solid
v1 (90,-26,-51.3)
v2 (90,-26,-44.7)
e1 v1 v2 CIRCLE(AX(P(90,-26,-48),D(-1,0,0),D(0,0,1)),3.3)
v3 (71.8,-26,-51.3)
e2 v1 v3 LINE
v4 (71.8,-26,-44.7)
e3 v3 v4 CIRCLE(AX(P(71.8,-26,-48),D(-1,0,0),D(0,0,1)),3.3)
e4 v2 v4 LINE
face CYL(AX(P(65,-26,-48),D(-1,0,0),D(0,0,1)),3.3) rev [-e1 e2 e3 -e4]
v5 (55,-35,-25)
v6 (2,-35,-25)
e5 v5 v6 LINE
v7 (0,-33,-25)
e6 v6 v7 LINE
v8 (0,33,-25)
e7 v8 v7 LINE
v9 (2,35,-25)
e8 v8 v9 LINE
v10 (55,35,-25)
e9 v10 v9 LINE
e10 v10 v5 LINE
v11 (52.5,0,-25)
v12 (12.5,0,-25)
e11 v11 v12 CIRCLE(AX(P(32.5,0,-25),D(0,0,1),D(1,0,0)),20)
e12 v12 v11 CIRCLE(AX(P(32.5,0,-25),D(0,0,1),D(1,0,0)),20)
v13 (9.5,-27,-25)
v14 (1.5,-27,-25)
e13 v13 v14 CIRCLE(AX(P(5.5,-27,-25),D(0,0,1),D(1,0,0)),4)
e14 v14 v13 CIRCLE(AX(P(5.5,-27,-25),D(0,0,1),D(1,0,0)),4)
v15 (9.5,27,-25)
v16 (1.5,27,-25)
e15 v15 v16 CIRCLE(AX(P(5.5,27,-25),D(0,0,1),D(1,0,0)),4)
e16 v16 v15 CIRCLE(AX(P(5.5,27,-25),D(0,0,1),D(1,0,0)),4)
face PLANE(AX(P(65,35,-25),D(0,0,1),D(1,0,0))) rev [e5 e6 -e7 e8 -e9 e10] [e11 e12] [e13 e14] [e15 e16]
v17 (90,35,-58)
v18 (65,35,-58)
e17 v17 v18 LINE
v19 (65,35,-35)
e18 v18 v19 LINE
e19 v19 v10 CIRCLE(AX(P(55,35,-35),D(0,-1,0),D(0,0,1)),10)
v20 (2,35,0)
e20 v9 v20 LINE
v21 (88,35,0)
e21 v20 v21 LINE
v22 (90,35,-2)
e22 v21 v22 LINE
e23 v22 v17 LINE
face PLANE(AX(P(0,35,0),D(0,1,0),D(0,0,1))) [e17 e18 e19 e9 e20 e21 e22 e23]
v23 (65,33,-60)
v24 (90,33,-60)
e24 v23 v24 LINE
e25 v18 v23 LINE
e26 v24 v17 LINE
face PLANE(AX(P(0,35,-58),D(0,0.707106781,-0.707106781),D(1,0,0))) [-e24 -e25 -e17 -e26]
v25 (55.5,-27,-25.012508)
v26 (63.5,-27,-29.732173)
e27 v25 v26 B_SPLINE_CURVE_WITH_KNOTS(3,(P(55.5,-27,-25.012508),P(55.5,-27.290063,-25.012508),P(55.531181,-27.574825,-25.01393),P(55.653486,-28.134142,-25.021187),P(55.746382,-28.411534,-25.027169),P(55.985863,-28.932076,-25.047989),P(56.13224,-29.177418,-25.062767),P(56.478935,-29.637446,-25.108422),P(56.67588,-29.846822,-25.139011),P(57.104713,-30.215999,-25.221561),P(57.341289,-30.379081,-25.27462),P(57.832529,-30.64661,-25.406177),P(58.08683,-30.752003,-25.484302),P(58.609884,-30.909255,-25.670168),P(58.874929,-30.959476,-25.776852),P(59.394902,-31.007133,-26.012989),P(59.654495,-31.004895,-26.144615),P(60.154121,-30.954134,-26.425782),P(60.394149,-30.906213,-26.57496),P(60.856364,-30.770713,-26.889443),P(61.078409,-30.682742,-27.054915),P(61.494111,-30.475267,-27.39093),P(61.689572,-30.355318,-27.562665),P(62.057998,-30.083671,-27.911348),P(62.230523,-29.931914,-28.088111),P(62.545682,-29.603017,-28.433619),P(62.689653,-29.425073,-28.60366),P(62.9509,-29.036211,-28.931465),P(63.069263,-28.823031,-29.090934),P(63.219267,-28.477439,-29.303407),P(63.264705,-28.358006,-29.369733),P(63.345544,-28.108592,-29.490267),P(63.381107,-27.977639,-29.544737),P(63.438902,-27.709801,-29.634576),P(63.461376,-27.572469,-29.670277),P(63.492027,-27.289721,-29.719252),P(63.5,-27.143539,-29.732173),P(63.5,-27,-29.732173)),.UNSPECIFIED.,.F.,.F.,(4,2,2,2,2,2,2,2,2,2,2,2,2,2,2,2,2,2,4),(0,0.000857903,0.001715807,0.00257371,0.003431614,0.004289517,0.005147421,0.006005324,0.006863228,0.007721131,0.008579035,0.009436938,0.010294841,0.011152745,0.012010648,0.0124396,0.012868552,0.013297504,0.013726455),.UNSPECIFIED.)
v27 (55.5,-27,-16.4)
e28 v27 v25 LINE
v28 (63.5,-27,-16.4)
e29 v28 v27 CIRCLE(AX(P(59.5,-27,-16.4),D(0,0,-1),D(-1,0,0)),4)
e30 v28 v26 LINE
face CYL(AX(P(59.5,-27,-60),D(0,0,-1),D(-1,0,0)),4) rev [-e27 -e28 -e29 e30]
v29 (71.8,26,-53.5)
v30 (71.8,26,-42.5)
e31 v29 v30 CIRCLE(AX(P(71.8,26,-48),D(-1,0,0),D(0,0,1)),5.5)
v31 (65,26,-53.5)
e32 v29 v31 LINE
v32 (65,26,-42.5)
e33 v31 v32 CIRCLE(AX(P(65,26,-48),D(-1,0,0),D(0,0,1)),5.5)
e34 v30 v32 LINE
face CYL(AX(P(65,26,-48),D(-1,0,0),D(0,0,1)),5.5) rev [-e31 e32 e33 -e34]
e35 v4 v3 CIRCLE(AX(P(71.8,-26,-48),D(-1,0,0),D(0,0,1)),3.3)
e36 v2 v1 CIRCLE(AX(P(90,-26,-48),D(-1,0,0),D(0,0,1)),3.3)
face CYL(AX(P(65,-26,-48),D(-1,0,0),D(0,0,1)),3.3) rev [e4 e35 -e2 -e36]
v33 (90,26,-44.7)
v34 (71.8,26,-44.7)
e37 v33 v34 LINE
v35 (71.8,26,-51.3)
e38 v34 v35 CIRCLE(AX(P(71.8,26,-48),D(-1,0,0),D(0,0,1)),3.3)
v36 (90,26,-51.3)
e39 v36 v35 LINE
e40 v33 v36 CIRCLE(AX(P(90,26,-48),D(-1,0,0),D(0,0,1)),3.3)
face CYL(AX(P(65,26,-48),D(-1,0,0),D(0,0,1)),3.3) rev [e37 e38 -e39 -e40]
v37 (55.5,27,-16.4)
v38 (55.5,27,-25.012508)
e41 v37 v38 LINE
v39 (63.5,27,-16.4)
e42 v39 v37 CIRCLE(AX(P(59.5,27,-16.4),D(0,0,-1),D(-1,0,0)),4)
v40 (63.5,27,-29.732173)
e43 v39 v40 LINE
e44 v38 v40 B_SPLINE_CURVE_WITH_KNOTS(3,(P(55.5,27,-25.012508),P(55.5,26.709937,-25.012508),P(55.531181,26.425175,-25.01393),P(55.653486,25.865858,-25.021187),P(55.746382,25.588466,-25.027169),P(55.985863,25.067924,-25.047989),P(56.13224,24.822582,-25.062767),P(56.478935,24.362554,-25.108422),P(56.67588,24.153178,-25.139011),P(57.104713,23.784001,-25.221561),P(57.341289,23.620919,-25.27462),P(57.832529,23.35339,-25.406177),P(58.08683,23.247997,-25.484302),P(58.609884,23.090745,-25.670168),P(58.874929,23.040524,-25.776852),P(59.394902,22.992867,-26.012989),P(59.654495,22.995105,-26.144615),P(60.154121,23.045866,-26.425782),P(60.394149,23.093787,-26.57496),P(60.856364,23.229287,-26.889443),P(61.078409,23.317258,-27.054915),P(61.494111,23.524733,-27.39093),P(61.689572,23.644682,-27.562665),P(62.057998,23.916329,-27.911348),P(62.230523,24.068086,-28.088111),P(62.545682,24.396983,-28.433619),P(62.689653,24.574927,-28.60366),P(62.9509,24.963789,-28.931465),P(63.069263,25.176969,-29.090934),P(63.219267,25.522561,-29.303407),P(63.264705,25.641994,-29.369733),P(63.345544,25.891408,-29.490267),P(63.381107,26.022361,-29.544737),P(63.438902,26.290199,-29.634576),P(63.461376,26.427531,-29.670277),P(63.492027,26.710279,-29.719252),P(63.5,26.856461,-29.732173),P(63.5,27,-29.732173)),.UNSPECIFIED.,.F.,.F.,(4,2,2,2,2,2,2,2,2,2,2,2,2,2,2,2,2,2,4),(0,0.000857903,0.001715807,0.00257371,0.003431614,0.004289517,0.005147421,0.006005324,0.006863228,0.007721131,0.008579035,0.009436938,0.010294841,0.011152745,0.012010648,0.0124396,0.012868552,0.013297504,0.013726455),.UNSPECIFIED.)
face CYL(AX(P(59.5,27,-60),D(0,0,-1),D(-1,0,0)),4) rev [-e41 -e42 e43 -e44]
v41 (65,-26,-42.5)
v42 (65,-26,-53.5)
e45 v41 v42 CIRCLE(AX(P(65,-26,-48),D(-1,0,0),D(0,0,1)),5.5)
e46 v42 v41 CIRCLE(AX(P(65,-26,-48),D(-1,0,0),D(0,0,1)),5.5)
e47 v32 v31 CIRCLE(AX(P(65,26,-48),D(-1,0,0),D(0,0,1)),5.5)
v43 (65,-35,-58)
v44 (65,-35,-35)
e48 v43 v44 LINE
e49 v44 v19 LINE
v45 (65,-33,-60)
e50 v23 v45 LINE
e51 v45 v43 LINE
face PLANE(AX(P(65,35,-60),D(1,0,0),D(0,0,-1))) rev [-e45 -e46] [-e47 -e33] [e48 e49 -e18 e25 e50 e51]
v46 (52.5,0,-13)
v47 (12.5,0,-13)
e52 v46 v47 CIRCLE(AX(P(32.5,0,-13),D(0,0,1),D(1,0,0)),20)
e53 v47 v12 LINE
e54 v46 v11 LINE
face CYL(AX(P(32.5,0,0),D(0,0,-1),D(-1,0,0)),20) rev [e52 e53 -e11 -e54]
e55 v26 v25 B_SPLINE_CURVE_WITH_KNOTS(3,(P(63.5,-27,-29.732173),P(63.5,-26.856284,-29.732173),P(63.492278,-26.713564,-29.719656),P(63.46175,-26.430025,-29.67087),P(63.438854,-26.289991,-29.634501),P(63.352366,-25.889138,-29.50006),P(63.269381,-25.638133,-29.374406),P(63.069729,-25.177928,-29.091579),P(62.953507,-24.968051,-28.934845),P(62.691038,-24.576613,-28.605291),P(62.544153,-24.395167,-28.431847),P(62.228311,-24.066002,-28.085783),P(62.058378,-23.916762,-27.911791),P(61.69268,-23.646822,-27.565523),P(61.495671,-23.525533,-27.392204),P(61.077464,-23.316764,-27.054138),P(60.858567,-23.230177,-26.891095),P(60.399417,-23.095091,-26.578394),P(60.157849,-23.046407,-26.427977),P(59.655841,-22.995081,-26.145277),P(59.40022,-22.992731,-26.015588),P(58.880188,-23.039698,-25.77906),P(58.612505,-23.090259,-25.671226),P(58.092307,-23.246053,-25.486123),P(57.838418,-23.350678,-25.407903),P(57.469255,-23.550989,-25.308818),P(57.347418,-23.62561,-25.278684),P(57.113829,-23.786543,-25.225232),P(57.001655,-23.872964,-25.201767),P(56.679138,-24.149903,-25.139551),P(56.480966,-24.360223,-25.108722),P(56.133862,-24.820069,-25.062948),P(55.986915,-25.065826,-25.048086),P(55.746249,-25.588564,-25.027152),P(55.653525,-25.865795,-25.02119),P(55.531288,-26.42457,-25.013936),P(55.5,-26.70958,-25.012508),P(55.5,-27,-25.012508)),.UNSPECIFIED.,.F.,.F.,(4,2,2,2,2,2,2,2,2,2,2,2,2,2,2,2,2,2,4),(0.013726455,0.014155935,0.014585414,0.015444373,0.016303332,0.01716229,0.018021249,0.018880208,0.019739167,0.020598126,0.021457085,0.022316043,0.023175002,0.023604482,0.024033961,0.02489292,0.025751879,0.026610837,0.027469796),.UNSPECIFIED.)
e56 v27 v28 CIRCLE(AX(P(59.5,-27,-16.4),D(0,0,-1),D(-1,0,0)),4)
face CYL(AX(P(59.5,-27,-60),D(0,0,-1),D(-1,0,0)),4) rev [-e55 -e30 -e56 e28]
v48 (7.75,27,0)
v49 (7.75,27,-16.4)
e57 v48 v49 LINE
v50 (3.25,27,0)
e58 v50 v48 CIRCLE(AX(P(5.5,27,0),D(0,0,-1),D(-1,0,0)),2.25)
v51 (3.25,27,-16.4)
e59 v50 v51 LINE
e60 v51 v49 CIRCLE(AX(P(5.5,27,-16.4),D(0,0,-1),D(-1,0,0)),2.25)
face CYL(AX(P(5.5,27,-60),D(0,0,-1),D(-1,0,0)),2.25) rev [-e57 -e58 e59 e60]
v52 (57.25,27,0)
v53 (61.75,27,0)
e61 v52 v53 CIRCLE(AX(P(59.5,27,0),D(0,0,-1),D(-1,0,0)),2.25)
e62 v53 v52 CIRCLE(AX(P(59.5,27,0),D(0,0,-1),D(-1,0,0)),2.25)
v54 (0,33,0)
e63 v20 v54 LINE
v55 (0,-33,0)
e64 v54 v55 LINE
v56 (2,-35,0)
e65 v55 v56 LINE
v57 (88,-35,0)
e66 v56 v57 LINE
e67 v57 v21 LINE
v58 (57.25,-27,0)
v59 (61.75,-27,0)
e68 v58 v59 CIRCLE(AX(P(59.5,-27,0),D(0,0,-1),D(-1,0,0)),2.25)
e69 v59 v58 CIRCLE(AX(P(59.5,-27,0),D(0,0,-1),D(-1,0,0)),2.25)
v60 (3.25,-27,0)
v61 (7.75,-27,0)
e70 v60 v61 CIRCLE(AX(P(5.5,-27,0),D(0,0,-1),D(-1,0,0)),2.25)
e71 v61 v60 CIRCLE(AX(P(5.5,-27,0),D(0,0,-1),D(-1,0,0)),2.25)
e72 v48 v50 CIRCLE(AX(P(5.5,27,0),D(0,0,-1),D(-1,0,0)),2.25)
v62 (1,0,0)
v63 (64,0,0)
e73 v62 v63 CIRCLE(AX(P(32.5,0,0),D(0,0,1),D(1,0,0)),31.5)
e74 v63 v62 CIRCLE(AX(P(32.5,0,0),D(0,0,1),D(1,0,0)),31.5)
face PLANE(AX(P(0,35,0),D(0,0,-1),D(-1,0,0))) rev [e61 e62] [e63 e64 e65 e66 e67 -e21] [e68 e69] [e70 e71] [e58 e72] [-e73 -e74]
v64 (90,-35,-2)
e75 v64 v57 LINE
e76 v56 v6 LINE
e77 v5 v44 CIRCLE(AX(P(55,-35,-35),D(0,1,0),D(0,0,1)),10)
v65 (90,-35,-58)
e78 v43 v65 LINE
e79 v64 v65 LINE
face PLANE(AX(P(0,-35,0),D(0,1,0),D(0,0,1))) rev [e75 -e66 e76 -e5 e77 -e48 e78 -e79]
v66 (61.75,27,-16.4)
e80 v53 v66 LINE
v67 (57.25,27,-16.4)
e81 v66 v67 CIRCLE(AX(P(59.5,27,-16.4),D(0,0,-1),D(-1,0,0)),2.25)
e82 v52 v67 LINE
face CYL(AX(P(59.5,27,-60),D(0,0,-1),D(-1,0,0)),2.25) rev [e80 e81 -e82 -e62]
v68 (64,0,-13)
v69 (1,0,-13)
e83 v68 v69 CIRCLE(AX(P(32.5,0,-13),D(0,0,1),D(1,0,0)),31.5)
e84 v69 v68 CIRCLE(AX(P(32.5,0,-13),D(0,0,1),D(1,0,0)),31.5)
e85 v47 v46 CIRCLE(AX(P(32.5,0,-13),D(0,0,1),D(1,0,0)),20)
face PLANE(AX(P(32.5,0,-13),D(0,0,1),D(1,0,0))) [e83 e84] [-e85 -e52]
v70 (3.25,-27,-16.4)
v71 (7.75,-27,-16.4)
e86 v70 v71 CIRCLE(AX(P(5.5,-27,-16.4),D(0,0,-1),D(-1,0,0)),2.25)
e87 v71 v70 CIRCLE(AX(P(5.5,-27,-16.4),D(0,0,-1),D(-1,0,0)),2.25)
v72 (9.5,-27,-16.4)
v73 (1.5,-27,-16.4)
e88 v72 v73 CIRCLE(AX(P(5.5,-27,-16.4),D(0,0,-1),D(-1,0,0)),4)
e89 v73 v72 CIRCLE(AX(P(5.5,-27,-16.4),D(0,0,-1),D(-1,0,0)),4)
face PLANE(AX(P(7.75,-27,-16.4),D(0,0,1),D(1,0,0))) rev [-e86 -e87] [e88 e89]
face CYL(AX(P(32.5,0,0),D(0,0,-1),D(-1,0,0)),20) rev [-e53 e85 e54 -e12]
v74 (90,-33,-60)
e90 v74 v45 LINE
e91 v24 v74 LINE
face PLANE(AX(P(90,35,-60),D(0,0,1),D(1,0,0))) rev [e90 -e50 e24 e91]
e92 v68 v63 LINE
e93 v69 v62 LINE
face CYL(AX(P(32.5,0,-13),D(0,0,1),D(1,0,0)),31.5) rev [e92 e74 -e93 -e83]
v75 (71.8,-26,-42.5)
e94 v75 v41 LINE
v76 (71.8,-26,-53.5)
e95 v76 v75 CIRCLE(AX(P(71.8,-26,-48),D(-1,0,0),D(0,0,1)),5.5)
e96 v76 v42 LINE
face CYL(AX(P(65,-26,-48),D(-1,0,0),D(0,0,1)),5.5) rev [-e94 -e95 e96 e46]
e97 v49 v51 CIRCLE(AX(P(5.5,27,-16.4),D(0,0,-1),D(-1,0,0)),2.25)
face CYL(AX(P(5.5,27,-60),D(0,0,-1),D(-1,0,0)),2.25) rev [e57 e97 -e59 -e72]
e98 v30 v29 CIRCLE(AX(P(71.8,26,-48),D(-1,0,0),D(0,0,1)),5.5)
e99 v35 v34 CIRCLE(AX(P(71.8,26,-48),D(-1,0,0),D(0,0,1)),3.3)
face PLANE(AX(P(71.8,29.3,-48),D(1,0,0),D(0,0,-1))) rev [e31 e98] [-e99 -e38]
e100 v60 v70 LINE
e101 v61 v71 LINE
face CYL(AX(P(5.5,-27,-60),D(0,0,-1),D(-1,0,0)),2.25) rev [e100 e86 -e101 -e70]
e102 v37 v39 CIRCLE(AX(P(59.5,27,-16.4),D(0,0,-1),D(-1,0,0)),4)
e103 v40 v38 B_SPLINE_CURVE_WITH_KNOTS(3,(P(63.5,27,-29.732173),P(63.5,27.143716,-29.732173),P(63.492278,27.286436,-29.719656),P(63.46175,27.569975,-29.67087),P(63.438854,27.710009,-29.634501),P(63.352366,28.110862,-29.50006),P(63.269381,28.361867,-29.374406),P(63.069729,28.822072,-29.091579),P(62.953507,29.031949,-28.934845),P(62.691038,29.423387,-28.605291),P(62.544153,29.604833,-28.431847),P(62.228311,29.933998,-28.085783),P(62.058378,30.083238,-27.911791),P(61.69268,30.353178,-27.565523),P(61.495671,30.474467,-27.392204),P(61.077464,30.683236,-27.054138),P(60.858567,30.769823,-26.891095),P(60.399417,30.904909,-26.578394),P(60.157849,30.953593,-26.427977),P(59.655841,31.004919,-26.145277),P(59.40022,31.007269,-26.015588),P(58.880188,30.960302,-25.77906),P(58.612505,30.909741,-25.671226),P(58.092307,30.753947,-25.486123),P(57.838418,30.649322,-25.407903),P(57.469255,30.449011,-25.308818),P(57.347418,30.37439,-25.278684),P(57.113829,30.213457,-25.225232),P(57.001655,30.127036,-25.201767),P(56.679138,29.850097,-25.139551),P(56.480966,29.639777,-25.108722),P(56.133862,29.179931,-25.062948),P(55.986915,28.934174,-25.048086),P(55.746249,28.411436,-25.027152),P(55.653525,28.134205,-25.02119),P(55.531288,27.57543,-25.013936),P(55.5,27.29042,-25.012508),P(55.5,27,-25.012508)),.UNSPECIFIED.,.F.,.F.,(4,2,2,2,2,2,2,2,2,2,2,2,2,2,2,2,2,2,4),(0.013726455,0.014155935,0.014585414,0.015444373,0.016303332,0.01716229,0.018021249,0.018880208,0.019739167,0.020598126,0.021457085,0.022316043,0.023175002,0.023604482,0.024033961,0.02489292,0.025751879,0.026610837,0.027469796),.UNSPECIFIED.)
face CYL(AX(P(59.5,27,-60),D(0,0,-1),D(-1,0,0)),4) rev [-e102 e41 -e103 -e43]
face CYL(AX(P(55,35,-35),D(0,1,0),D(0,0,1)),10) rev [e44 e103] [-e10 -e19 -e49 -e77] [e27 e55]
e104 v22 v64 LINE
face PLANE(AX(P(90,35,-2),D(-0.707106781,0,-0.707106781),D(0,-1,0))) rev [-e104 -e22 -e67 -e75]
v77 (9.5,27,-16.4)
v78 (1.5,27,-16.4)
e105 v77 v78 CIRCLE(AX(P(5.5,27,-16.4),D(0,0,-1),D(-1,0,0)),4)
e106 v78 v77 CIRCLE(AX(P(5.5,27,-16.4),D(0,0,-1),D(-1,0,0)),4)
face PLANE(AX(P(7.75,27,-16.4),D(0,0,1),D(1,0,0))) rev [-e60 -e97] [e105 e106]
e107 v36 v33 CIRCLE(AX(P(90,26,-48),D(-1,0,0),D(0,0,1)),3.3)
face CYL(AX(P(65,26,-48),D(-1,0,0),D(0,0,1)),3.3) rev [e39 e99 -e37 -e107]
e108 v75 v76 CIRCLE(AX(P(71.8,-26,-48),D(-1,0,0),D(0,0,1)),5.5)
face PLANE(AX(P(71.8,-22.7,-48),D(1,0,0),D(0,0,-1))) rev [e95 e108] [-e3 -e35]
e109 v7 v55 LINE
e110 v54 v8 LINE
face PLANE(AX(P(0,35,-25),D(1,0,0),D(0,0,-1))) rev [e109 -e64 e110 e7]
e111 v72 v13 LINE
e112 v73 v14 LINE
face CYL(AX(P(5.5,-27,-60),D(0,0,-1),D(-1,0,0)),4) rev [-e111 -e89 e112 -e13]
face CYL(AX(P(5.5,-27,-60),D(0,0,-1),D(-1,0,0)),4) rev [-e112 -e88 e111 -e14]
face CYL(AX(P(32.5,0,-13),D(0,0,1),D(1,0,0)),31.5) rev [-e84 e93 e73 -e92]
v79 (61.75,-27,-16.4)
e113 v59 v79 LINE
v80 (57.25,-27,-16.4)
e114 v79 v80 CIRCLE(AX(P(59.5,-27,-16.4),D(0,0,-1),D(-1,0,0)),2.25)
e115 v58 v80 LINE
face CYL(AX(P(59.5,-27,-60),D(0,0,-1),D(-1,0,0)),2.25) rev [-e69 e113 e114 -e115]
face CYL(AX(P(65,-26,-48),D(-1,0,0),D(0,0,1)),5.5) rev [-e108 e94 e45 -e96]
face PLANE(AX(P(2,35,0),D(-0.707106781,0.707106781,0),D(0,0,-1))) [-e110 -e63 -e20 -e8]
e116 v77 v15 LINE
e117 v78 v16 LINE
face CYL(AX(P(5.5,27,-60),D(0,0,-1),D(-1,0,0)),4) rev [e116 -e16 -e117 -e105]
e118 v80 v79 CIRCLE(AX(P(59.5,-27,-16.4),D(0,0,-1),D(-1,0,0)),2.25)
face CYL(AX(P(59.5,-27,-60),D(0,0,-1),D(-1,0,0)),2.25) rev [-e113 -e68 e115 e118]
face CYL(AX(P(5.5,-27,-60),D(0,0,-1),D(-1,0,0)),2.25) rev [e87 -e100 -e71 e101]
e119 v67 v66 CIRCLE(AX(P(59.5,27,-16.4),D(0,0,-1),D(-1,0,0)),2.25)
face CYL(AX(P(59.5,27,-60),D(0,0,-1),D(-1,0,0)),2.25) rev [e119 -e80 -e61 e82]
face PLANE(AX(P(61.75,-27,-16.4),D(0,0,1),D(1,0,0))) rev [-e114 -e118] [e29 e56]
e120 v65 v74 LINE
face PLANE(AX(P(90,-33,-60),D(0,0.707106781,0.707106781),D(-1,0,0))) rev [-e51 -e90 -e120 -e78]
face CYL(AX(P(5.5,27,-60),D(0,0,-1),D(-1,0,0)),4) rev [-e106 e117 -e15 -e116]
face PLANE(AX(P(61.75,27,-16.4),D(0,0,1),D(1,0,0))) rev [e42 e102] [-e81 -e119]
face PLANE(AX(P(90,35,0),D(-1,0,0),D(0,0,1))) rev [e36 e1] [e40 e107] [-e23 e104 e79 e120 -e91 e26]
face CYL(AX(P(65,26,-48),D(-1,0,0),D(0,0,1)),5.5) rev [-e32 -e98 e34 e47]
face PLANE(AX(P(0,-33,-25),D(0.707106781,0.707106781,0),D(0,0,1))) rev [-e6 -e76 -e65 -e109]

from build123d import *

# Parameters (mm, degrees)
EXTRUDE_1_DEPTH              = 35
FILLET_1_R                   = 10
SKETCH_2_R                   = 31.5
CUT_EXTRUDE_1_DEPTH          = 13
CUT_EXTRUDE_2_DEPTH          = 103.713192921
CUT_EXTRUDE_2_DEPTH_BACK     = 103.713192921
SKETCH_3_R                   = 20
HOLE_WIZARD_M6_1_D           = 6.6
HOLE_WIZARD_M6_1_CBORE_D     = 11
HOLE_WIZARD_M6_1_CBORE_DEPTH = 6.8
CHAMFER_1_SIZE               = 2
HOLE_WIZARD_M4_1_D           = 4.5
HOLE_WIZARD_M4_1_CBORE_D     = 8
HOLE_WIZARD_M4_1_CBORE_DEPTH = 43.6


with BuildPart() as part:
    # 草图1 → 凸台-拉伸1 (new, symmetric)
    with BuildSketch(Plane(origin=(0, 0, 0), x_dir=(1, 0, 0), z_dir=(0, 1, 0))):
        Polygon((0, 0), (90, 0), (90, 60), (65, 60), (65, 25), (0, 25), align=None)
    extrude(amount=EXTRUDE_1_DEPTH, both=True)

    # 圆角1
    fillet_1_edges = [part.edges().sort_by_distance(p)[0] for p in [
        (65, 0, -25),
    ]]
    fillet(fillet_1_edges, radius=FILLET_1_R)

    # 草图2 → 切除-拉伸1 (cut)
    with BuildSketch(Plane.XY):
        with Locations((32.5, 0)):
            Circle(SKETCH_2_R)
    extrude(amount=-CUT_EXTRUDE_1_DEPTH, mode=Mode.SUBTRACT)

    # 草图3 → 切除-拉伸2 (cut, two sides: drawn at the far end of the back side and taken through both)
    with BuildSketch(Plane(origin=(0, 0, -25), x_dir=(-1, 0, 0), z_dir=(0, 0, -1)).offset(-CUT_EXTRUDE_2_DEPTH_BACK)):
        with Locations((-32.5, 0)):
            Circle(SKETCH_3_R)
    extrude(amount=CUT_EXTRUDE_2_DEPTH + CUT_EXTRUDE_2_DEPTH_BACK, mode=Mode.SUBTRACT)

    # M6 六角圆柱头螺钉的柱形沉头孔1 (through all)
    with Locations(Plane.ZY.offset(-65)):
        with Locations((-48, 26), (-48, -26)):
            CounterBoreHole(HOLE_WIZARD_M6_1_D / 2, HOLE_WIZARD_M6_1_CBORE_D / 2, HOLE_WIZARD_M6_1_CBORE_DEPTH)

    # 倒角1
    chamfer_1_edges = [part.edges().sort_by_distance(p)[0] for p in [
        (90, 0, 0),
        (77.5, 35, -60),
        (0, 35, -12.5),
        (77.5, -35, -60),
        (0, -35, -12.5),
    ]]
    chamfer(chamfer_1_edges, length=CHAMFER_1_SIZE)

    # M4 六角圆柱头螺钉的柱形沉头孔1 (through all)
    with Locations(Plane(origin=(0, 0, -60), x_dir=(-1, 0, 0), z_dir=(0, 0, -1))):
        with Locations((-5.5, 27), (-59.5, 27), (-59.5, -27), (-5.5, -27)):
            CounterBoreHole(HOLE_WIZARD_M4_1_D / 2, HOLE_WIZARD_M4_1_CBORE_D / 2, HOLE_WIZARD_M4_1_CBORE_DEPTH)


solid = part.part
